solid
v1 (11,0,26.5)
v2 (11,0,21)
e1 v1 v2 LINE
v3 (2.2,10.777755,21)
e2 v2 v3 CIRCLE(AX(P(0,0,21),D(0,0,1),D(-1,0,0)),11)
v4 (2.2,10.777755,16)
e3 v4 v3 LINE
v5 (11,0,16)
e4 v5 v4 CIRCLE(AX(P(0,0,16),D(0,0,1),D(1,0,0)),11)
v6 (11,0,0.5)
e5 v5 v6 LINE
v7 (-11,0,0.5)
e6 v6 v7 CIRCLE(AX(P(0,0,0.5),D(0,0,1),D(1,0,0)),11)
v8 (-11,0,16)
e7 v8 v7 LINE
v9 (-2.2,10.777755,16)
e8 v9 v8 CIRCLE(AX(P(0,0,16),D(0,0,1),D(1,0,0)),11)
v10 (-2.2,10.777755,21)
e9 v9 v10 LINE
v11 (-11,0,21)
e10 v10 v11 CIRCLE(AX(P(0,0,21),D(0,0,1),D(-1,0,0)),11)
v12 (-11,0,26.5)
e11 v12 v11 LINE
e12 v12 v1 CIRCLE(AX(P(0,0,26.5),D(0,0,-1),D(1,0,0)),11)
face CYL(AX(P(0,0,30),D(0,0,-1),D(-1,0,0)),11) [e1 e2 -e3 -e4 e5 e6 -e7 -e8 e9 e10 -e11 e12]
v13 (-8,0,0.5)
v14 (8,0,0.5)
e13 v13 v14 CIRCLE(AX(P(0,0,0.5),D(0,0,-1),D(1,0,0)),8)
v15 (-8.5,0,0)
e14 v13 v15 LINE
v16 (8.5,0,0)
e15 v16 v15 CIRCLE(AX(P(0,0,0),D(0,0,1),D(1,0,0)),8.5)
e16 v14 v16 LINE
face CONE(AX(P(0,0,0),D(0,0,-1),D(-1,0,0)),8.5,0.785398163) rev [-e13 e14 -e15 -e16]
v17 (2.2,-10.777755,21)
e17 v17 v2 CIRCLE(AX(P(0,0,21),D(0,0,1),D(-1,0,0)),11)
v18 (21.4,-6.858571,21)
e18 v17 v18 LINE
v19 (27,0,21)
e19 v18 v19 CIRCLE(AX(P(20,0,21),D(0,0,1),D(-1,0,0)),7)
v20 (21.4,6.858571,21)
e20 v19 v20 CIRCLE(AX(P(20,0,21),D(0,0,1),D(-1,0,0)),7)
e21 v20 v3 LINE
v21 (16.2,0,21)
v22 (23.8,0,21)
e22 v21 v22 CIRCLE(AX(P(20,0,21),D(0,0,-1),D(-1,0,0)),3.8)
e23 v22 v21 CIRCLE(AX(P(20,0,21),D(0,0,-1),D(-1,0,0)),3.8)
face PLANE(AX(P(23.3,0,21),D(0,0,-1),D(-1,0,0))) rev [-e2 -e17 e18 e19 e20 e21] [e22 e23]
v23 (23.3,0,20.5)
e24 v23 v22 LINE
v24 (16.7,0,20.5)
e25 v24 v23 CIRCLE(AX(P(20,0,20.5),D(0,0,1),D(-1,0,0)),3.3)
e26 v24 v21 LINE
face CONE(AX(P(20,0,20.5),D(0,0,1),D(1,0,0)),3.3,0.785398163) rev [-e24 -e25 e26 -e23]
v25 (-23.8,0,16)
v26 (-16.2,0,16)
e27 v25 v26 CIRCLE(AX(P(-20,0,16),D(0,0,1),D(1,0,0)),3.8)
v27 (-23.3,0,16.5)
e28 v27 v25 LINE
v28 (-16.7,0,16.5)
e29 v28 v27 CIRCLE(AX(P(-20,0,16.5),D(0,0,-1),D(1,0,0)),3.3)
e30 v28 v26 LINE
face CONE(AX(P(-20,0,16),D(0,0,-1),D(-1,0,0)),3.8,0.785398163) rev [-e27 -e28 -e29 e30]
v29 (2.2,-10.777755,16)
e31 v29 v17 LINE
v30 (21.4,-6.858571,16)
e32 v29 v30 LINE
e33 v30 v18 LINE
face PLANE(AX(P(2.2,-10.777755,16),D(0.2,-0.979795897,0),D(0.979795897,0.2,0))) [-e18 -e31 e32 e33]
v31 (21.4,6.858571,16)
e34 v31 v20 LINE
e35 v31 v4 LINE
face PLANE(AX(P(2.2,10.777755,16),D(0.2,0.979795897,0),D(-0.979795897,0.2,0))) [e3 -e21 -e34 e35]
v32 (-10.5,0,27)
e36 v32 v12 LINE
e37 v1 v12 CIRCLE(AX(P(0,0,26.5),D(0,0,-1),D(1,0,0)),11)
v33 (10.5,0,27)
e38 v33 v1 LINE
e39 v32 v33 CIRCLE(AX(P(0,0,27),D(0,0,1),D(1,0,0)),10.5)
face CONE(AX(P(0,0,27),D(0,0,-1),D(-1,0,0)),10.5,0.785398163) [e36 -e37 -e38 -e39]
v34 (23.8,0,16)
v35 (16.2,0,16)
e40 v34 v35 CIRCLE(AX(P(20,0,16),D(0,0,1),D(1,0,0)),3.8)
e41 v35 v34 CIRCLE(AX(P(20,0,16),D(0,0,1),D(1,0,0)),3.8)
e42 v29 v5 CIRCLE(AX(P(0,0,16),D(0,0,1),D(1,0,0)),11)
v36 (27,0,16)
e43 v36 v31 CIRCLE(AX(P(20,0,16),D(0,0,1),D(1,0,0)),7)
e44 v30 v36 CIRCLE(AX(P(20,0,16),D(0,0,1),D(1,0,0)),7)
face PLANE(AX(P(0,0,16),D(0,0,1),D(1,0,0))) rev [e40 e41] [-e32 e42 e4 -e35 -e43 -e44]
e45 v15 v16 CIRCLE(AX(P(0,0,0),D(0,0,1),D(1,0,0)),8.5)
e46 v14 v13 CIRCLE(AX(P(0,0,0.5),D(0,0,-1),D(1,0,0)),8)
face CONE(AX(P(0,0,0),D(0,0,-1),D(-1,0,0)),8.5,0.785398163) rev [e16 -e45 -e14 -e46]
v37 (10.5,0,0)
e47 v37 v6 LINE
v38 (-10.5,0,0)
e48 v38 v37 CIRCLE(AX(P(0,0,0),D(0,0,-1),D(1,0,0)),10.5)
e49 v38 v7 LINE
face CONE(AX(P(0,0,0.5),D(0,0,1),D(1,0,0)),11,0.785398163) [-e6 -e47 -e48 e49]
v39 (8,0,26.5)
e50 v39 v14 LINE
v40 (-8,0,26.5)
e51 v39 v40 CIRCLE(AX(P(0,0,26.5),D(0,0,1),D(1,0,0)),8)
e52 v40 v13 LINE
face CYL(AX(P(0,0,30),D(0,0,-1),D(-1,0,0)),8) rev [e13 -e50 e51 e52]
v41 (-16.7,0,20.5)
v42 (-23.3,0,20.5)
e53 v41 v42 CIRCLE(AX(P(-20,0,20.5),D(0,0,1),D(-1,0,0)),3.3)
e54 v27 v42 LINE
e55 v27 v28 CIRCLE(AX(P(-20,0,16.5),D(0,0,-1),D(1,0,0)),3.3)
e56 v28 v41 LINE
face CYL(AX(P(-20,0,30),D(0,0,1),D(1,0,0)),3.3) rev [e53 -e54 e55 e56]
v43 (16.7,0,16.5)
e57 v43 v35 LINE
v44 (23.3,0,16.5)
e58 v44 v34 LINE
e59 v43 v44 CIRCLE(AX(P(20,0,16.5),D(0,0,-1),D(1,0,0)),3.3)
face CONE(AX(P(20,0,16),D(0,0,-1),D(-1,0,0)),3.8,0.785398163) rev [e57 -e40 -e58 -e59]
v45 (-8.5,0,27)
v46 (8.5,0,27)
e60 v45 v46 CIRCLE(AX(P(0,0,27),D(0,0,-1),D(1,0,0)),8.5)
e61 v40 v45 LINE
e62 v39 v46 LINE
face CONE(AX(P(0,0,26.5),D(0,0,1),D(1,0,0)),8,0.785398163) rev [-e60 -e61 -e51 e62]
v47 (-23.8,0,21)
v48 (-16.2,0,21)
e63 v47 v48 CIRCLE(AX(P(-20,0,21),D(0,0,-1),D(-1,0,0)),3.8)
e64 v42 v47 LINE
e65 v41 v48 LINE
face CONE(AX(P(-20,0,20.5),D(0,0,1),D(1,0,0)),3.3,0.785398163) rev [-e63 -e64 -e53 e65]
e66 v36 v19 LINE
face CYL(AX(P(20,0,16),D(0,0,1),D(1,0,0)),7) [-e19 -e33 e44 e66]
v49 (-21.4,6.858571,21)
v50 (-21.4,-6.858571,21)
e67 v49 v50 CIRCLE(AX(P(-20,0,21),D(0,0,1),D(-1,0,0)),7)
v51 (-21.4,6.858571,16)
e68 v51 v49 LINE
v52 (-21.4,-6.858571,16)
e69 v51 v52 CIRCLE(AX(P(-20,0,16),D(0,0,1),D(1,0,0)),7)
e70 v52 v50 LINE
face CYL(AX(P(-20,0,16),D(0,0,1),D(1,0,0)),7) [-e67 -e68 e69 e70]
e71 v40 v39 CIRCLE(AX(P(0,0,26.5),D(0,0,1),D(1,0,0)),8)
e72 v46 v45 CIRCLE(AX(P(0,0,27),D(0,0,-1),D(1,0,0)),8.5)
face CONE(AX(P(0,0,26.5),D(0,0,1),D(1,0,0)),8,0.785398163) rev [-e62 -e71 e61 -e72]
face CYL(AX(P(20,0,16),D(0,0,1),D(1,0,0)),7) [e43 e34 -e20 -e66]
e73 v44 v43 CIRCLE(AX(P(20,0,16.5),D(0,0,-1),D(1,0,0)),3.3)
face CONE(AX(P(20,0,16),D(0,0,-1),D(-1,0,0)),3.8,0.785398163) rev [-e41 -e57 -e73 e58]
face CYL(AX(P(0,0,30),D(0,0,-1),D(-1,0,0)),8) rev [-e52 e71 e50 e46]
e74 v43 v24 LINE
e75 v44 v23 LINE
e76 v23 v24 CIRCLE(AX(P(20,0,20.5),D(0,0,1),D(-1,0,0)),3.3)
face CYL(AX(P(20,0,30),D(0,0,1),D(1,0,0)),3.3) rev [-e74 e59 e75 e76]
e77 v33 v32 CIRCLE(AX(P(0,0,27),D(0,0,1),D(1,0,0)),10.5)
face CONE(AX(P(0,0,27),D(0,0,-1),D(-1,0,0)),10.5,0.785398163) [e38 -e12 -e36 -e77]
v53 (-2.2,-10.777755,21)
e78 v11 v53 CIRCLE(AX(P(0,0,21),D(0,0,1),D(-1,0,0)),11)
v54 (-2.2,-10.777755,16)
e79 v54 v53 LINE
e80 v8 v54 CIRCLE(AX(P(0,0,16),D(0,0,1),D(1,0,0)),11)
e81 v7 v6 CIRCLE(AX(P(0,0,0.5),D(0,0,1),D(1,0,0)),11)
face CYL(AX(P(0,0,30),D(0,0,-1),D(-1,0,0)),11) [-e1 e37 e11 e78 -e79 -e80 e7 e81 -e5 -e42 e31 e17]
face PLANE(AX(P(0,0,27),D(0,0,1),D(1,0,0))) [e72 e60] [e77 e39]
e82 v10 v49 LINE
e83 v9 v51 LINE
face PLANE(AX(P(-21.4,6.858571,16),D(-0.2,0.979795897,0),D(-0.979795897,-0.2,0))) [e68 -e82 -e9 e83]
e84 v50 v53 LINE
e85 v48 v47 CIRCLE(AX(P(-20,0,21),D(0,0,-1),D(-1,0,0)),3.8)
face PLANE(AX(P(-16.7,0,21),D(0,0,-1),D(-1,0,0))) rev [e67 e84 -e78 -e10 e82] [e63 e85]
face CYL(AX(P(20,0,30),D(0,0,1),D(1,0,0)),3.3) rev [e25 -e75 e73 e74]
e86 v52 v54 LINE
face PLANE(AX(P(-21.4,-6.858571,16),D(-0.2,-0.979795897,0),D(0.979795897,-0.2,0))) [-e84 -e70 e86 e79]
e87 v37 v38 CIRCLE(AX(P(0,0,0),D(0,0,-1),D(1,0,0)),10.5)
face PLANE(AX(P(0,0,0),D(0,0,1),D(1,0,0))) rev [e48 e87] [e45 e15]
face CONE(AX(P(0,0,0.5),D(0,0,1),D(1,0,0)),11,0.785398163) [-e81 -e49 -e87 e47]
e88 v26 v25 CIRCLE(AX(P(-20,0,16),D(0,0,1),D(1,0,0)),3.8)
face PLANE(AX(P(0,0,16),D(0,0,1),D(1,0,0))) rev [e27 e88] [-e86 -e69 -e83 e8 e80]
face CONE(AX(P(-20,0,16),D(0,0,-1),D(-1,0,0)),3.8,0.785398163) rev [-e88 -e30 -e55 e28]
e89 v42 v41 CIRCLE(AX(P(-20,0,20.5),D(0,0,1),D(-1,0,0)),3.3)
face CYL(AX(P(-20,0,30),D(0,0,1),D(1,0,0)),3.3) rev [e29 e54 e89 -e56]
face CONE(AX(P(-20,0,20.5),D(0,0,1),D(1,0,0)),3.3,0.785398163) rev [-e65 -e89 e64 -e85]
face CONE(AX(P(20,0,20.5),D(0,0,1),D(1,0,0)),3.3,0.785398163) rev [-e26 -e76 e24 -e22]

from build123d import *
from build123d.topology import SkipClean

# Parameters (mm, degrees)
SKETCH1_R                                            = 11
SKETCH1_R_2                                          = 8
BOSS_EXTRUDE1_DEPTH                                  = 30
BOSS_EXTRUDE2_START                                  = -14
SKETCH2_R                                            = 8
BOSS_EXTRUDE2_DEPTH                                  = 14
HOLE_SIZE_PER_SOCKET_HEAD_CAP_SCREW_TYPE_D           = 6.6
HOLE_SIZE_PER_SOCKET_HEAD_CAP_SCREW_TYPE_CBORE_D     = 15
HOLE_SIZE_PER_SOCKET_HEAD_CAP_SCREW_TYPE_CBORE_DEPTH = 9
SKETCH5_OUTSIDE_W                                    = 69.114
SKETCH5_OUTSIDE_H                                    = 37.114
SKETCH5_OUTSIDE_R                                    = 11
CUT_EXTRUDE2_DEPTH                                   = 9
CUT_EXTRUDE3_START                                   = -3
SKETCH6_R                                            = 11
CUT_EXTRUDE3_DEPTH                                   = 3
CHAMFER1_SIZE                                        = 0.5


with BuildPart() as part:
    # Sketch1 → Boss-Extrude1 (new body)
    with BuildSketch(Plane.XY):
        Circle(SKETCH1_R)
        Circle(SKETCH1_R_2, mode=Mode.SUBTRACT)
    extrude(amount=BOSS_EXTRUDE1_DEPTH)

    # Sketch2 → Boss-Extrude2 (add)
    with SkipClean():  # the faces are left unmerged after this step: merging them gives an invalid solid
        with BuildSketch(Plane.XY.offset(30).offset(BOSS_EXTRUDE2_START)):
            with BuildLine():
                Line((-21.4, 6.858571), (-2.2, 10.777755))
                ThreePointArc((-2.2, 10.777755), (0, 11), (2.2, 10.777755))
                Line((2.2, 10.777755), (21.4, 6.858571))
                ThreePointArc((21.4, 6.858571), (27, 0), (21.4, -6.858571))
                Line((21.4, -6.858571), (2.2, -10.777755))
                ThreePointArc((2.2, -10.777755), (0, -11), (-2.2, -10.777755))
                Line((-2.2, -10.777755), (-21.4, -6.858571))
                ThreePointArc((-21.4, -6.858571), (-27, 0), (-21.4, 6.858571))
            make_face()
            Circle(SKETCH2_R, mode=Mode.SUBTRACT)
        extrude(amount=BOSS_EXTRUDE2_DEPTH)

    # Hole size per socket head cap screw type1 (through all)
    with Locations(Plane(origin=(-20, 0, 30), x_dir=(1, 0, 0), z_dir=(0, 0, 1))):
        with Locations((0, 0), (40, 0)):
            CounterBoreHole(HOLE_SIZE_PER_SOCKET_HEAD_CAP_SCREW_TYPE_D / 2, HOLE_SIZE_PER_SOCKET_HEAD_CAP_SCREW_TYPE_CBORE_D / 2, HOLE_SIZE_PER_SOCKET_HEAD_CAP_SCREW_TYPE_CBORE_DEPTH)

    # Sketch5 outside → Cut-Extrude2 (cut)
    with SkipClean():  # the faces are left unmerged after this step: merging them gives an invalid solid
        with BuildSketch(Plane.XY.offset(30)):
            Rectangle(SKETCH5_OUTSIDE_W, SKETCH5_OUTSIDE_H)
            Circle(SKETCH5_OUTSIDE_R, mode=Mode.SUBTRACT)
        extrude(amount=-CUT_EXTRUDE2_DEPTH, mode=Mode.SUBTRACT)

    # Sketch6 → Cut-Extrude3 (cut)
    with SkipClean():  # the faces are left unmerged after this step: merging them gives an invalid solid
        with BuildSketch(Plane.XY.offset(30).offset(CUT_EXTRUDE3_START)):
            Circle(SKETCH6_R)
        extrude(amount=CUT_EXTRUDE3_DEPTH, mode=Mode.SUBTRACT)

    # Chamfer1
    chamfer1_edges = [part.edges().sort_by_distance(p)[0] for p in [
        (8.520563, 6.957011, 27),
        (-8, 0, 27),
        (-11, 0, 0),
        (23.3, 0, 16),
        (23.3, 0, 21),
        (-8, 0, 0),
        (-16.7, 0, 16),
        (-16.7, 0, 21),
    ]]
    chamfer(chamfer1_edges, length=CHAMFER1_SIZE)


solid = part.part
